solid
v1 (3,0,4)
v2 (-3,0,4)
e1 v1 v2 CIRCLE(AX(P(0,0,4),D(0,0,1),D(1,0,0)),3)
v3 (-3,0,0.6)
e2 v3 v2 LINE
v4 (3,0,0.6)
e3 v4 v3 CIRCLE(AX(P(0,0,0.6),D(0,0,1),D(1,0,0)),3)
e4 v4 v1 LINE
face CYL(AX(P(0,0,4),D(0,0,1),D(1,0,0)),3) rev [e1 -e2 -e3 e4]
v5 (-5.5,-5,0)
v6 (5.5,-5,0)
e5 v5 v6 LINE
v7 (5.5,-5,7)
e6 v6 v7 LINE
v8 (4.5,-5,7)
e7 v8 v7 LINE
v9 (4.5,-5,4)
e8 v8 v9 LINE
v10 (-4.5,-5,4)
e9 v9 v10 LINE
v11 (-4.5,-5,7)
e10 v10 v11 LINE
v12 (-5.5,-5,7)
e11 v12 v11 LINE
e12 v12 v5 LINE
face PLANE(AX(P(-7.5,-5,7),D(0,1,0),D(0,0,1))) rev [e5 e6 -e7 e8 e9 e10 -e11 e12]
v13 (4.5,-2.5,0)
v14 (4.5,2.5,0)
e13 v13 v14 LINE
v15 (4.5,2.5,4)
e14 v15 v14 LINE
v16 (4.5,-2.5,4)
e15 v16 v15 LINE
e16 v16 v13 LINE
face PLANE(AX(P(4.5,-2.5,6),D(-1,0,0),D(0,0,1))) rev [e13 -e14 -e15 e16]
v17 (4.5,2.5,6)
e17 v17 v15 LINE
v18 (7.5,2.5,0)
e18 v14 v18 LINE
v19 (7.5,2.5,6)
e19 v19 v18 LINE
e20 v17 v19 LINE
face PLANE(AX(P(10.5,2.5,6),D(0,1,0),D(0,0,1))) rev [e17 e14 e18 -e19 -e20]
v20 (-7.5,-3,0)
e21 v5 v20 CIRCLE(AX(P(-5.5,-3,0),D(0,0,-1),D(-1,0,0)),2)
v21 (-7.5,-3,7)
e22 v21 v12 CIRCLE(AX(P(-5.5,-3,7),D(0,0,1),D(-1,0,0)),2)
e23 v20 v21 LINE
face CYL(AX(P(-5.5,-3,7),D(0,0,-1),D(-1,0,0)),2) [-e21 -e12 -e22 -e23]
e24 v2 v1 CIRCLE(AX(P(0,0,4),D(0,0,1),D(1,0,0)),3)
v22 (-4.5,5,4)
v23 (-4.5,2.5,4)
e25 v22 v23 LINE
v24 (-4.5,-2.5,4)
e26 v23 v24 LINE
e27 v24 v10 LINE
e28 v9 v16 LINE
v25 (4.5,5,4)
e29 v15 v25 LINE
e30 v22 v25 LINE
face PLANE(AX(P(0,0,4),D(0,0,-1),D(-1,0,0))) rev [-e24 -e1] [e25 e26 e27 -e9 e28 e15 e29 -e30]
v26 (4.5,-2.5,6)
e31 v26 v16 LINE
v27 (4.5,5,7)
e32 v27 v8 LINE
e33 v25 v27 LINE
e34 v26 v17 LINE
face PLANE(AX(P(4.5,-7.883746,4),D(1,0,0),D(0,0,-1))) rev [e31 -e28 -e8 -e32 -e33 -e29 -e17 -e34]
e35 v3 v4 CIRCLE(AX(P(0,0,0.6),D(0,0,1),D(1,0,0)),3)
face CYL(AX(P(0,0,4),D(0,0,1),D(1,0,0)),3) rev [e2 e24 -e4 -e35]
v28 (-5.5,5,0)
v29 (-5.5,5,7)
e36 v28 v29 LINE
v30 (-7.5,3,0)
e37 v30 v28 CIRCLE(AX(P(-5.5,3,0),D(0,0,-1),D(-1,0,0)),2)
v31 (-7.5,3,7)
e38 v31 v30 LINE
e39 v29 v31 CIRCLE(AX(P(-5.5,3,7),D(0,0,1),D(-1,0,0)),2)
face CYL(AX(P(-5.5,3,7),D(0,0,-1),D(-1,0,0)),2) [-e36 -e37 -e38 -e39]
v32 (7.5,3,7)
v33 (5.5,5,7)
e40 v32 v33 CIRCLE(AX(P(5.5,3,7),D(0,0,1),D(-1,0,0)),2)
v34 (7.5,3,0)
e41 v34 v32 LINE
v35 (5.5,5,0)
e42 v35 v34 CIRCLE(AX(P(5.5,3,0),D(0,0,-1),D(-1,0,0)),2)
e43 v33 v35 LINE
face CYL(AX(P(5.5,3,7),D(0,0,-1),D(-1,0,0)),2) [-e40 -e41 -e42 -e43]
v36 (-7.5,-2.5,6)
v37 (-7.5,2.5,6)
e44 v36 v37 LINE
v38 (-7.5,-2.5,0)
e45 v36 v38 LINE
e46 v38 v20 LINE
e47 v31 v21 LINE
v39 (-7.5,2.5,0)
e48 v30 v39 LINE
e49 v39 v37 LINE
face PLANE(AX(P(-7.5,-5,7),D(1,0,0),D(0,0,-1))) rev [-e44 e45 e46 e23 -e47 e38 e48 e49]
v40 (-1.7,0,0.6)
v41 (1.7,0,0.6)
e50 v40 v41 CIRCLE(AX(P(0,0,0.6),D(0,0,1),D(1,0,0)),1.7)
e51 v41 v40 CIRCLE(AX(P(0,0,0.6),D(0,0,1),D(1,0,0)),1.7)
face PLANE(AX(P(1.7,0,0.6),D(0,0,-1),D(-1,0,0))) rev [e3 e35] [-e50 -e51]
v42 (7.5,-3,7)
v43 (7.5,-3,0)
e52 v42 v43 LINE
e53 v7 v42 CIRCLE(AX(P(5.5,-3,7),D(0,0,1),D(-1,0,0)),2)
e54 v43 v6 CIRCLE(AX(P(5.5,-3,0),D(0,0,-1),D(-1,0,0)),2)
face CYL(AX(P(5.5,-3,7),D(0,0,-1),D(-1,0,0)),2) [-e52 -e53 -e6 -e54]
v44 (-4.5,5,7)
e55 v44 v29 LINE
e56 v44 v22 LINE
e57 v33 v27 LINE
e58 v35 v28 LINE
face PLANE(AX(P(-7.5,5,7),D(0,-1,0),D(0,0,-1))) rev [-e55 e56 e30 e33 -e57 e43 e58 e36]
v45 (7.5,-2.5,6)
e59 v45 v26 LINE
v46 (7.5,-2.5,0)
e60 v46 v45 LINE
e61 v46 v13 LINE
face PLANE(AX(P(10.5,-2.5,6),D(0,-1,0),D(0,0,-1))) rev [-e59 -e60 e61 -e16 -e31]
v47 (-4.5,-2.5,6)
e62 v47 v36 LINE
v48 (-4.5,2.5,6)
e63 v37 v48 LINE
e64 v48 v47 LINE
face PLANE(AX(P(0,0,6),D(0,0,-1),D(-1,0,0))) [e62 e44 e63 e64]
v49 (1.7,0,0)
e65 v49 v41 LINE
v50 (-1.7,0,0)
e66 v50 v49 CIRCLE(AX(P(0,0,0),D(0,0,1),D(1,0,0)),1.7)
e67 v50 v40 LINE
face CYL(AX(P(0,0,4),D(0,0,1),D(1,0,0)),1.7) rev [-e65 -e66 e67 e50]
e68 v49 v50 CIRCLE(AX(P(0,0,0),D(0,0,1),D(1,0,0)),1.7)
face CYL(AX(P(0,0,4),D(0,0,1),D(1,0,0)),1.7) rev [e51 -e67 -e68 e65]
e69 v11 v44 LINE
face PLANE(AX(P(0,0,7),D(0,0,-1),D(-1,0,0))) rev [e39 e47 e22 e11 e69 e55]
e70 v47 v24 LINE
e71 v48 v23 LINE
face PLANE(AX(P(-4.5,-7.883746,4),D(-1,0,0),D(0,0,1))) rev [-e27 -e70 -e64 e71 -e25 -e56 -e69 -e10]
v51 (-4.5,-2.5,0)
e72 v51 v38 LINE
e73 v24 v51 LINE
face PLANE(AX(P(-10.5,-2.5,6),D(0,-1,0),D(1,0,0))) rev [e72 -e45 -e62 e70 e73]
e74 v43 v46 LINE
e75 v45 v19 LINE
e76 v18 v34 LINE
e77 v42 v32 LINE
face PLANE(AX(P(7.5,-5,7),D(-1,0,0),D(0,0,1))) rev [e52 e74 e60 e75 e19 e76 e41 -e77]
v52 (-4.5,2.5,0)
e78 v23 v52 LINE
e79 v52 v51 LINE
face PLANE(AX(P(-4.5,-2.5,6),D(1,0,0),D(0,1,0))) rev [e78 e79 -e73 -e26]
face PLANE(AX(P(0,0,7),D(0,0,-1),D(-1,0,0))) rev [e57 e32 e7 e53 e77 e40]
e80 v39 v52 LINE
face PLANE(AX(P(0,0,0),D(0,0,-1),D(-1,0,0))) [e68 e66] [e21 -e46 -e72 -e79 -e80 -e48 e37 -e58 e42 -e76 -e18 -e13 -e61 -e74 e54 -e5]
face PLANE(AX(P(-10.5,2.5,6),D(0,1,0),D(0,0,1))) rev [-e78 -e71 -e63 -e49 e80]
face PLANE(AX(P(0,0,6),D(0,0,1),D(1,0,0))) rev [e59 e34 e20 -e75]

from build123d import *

# Parameters (mm, degrees)
SKETCH1_W                                            = 15
SKETCH1_H                                            = 10
BOSS_EXTRUDE1_DEPTH                                  = 7
SKETCH2_W                                            = 9
SKETCH2_H                                            = 15.767491366
CUT_EXTRUDE1_DEPTH                                   = 3
SKETCH4_W                                            = 6
SKETCH4_H                                            = 5
CUT_EXTRUDE3_DEPTH                                   = 6
HOLE_SIZE_PER_SOCKET_HEAD_CAP_SCREW_TYPE_D           = 3.4
HOLE_SIZE_PER_SOCKET_HEAD_CAP_SCREW_TYPE_CBORE_D     = 6
HOLE_SIZE_PER_SOCKET_HEAD_CAP_SCREW_TYPE_CBORE_DEPTH = 3.4
FILLET1_R                                            = 2


with BuildPart() as part:
    # Sketch1 → Boss-Extrude1 (new body)
    with BuildSketch(Plane.XY):
        Rectangle(SKETCH1_W, SKETCH1_H)
    extrude(amount=BOSS_EXTRUDE1_DEPTH)

    # Sketch2 → Cut-Extrude1 (cut)
    with BuildSketch(Plane.XY.offset(7)):
        Rectangle(SKETCH2_W, SKETCH2_H)
    extrude(amount=-CUT_EXTRUDE1_DEPTH, mode=Mode.SUBTRACT)

    # Sketch4 → Cut-Extrude3 (cut)
    with BuildSketch(Plane(origin=(0, 0, 0), x_dir=(-1, 0, 0), z_dir=(0, 0, -1))):
        with Locations((-7.5, 0)):
            Rectangle(SKETCH4_W, SKETCH4_H)
        with Locations((7.5, 0)):
            Rectangle(SKETCH4_W, SKETCH4_H)
    extrude(amount=-CUT_EXTRUDE3_DEPTH, mode=Mode.SUBTRACT)

    # Hole size per socket head cap screw type 1 (through all)
    with Locations(Plane.XY.offset(4)):
        with Locations((0, 0)):
            CounterBoreHole(HOLE_SIZE_PER_SOCKET_HEAD_CAP_SCREW_TYPE_D / 2, HOLE_SIZE_PER_SOCKET_HEAD_CAP_SCREW_TYPE_CBORE_D / 2, HOLE_SIZE_PER_SOCKET_HEAD_CAP_SCREW_TYPE_CBORE_DEPTH)

    # Fillet1
    fillet1_edges = [part.edges().sort_by_distance(p)[0] for p in [
        (7.5, -5, 3.5),
        (-7.5, -5, 3.5),
        (-7.5, 5, 3.5),
        (7.5, 5, 3.5),
    ]]
    fillet(fillet1_edges, radius=FILLET1_R)


solid = part.part
